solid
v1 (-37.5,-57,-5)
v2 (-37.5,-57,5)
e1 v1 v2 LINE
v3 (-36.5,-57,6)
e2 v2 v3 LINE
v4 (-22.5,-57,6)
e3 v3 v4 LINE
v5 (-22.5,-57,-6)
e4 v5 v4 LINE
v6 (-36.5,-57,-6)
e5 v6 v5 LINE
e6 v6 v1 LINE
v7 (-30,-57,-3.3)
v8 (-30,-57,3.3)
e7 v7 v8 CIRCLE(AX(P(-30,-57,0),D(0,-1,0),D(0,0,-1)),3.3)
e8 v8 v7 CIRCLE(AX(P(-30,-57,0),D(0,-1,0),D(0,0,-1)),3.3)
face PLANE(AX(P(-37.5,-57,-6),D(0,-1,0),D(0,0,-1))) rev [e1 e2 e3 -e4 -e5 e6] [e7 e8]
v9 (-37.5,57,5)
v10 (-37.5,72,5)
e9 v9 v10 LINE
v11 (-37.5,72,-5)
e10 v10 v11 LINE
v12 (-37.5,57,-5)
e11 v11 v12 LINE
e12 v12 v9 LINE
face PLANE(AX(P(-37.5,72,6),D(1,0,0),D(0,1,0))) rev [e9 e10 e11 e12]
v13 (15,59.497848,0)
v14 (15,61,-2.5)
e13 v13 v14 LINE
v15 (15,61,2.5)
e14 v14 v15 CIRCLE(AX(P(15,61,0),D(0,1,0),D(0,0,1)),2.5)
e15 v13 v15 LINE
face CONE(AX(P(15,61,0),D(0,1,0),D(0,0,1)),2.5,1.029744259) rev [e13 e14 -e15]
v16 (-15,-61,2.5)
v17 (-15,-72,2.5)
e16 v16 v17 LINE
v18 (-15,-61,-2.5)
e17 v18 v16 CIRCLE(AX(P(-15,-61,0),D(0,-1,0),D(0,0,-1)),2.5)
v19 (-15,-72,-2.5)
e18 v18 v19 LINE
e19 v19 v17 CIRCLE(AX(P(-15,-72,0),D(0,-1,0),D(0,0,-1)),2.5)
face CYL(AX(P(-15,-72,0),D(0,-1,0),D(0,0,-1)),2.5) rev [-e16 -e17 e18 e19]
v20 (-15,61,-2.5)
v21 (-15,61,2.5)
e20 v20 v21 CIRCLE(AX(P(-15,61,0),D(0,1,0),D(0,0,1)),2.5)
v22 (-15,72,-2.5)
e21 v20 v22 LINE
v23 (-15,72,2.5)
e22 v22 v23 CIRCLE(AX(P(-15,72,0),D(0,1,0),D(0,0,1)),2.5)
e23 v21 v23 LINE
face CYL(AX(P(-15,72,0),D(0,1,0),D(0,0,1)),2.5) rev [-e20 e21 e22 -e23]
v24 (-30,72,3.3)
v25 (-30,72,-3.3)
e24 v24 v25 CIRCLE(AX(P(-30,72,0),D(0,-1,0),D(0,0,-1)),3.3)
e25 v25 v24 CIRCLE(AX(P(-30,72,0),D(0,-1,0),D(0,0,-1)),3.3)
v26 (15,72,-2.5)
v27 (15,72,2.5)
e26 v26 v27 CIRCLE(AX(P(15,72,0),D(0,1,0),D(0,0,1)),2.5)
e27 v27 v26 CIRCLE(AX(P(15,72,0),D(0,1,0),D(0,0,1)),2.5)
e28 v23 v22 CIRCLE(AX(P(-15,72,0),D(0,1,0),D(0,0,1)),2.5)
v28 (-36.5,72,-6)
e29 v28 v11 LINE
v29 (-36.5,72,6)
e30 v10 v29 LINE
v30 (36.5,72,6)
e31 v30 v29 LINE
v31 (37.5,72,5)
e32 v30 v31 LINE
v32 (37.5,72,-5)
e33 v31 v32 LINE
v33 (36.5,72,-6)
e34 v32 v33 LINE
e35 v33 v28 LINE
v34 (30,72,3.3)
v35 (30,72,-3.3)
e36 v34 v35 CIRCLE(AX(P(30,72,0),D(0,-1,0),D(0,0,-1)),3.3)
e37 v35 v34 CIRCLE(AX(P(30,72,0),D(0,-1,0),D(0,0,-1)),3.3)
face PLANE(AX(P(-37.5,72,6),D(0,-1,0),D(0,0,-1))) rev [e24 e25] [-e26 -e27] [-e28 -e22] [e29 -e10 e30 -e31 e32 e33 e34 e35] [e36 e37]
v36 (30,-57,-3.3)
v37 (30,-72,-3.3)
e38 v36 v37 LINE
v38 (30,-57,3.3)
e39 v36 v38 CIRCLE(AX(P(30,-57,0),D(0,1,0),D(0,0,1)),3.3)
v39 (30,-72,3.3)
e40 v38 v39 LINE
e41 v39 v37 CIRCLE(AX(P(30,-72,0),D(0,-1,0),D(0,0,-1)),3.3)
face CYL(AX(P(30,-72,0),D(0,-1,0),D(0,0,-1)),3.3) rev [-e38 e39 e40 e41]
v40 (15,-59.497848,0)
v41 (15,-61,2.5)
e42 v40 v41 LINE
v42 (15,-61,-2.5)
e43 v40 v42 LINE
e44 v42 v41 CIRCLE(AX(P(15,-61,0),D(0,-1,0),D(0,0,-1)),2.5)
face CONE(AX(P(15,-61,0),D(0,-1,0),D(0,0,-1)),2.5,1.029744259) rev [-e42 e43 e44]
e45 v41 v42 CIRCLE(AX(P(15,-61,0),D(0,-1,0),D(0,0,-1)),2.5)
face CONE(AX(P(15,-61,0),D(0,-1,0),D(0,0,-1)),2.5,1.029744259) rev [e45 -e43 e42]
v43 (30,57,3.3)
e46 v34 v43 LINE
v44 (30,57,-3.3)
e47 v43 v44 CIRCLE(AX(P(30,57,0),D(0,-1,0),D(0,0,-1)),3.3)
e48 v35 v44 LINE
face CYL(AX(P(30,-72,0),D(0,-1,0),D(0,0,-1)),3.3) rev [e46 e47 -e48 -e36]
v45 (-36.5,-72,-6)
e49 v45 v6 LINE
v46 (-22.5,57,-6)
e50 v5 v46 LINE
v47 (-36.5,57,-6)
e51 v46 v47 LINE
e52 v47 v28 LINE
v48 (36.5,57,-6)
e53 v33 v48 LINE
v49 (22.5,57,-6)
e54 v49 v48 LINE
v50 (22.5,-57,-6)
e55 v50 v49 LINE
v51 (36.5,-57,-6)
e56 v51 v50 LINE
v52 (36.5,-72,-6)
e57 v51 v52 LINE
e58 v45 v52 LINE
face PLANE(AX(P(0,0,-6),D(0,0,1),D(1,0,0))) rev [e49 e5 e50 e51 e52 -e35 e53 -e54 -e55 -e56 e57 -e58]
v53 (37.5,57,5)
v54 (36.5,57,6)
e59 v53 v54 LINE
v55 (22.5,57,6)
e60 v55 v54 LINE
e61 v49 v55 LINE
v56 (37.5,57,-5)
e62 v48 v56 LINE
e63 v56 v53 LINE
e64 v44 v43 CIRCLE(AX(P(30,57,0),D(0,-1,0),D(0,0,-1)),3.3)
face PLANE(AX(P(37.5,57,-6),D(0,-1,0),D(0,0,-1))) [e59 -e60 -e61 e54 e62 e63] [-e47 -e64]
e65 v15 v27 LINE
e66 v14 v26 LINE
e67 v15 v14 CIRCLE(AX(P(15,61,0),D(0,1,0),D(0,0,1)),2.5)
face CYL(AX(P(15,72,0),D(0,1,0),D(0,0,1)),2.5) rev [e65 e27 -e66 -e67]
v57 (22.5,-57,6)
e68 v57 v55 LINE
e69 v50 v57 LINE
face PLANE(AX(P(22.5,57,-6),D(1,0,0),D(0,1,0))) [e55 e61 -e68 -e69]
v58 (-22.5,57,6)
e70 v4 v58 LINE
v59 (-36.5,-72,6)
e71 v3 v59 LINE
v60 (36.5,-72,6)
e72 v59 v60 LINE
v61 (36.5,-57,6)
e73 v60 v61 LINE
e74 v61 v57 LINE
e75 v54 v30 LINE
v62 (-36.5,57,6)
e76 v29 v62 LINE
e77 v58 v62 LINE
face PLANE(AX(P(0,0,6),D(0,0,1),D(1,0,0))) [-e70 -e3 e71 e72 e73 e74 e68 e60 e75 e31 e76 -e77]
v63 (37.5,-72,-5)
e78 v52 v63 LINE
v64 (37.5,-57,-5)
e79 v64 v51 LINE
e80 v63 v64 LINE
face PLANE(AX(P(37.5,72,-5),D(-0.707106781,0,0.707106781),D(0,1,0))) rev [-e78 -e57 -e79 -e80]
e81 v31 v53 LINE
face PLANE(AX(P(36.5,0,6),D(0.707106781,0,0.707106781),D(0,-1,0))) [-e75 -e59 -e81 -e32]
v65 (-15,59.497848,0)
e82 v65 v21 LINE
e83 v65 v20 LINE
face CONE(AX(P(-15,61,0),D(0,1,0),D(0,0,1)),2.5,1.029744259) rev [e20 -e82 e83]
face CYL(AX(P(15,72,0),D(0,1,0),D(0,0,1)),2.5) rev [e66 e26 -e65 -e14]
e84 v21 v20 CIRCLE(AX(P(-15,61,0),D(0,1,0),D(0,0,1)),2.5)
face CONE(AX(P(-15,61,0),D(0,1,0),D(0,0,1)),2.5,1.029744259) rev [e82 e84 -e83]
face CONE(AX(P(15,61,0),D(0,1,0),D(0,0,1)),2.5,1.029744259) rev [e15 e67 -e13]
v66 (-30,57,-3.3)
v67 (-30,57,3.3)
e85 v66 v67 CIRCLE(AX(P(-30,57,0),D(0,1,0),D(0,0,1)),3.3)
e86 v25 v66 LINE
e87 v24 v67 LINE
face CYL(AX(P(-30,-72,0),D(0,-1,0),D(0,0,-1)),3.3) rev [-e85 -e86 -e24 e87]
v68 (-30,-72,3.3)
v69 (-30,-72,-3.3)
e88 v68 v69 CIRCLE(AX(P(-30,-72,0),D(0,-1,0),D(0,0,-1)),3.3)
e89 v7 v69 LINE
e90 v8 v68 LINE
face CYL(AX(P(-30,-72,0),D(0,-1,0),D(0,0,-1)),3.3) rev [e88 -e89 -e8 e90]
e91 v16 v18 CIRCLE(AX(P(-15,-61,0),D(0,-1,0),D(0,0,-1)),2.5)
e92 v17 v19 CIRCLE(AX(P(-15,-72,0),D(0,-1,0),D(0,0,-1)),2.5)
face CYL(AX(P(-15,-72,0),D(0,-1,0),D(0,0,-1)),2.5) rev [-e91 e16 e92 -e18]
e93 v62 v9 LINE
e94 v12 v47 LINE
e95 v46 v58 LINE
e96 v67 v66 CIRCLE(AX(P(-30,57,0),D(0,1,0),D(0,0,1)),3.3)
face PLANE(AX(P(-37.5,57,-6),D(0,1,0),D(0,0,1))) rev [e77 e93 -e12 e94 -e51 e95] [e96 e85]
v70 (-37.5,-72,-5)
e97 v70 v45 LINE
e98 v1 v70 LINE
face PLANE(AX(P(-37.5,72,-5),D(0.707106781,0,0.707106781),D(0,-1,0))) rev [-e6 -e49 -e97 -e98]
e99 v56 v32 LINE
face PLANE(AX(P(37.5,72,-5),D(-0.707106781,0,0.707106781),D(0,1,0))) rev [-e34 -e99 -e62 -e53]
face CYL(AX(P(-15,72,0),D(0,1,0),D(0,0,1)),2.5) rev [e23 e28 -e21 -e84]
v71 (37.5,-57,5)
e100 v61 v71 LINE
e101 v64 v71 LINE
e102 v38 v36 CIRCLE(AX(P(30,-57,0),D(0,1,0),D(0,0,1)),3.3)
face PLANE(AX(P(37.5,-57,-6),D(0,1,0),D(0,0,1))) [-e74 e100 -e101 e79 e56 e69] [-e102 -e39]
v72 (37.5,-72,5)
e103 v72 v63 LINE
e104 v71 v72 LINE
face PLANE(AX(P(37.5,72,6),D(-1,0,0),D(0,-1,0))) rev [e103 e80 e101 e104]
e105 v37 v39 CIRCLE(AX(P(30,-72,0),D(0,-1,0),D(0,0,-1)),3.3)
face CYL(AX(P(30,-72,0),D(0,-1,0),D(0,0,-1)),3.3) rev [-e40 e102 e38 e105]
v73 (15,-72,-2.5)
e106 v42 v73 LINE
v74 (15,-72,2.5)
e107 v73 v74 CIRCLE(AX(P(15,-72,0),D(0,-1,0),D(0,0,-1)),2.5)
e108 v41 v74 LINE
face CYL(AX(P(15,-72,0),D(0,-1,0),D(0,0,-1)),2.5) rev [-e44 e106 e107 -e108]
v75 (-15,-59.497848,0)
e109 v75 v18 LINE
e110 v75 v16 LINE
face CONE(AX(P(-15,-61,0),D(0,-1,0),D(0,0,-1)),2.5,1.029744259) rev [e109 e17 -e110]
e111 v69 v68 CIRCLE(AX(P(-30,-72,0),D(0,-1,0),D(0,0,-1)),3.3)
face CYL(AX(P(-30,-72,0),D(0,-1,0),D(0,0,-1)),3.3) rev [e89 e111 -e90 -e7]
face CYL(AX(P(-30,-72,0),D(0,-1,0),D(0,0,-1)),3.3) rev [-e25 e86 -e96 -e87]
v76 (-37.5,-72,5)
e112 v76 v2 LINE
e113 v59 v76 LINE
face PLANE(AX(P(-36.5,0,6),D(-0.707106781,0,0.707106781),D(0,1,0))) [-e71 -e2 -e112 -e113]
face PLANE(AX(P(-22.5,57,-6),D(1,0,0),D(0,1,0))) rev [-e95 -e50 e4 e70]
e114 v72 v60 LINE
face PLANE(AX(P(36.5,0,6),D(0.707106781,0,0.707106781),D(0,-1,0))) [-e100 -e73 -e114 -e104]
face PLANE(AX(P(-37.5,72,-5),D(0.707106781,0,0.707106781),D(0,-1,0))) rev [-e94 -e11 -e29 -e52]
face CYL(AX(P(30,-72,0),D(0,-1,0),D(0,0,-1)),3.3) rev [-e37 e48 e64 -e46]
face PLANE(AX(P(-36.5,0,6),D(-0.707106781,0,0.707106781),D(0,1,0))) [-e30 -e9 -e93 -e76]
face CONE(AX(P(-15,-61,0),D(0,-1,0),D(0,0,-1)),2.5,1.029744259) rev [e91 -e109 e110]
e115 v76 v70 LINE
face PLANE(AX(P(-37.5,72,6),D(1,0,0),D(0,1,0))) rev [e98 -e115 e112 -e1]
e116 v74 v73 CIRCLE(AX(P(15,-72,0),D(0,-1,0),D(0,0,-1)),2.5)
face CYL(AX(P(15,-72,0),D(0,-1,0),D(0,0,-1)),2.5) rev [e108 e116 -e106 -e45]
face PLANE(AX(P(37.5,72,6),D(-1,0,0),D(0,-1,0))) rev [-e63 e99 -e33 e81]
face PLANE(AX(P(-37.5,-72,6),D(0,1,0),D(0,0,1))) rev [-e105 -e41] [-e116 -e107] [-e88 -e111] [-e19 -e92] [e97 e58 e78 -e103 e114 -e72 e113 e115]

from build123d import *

# Parameters (mm, degrees)
SKETCH1_W                          = 75
SKETCH1_H                          = 144
BOSS_EXTRUDE1_DEPTH                = 6
SKETCH4_W                          = 15
SKETCH4_H                          = 114
CUT_EXTRUDE1_DEPTH                 = 83.0624762
F_6_6_6_6_DIAMETER_HOLE1_D         = 6.6
BLIND_PIN_HOLE1_SIZE_MM_AT_2_COUNT = 2
BLIND_PIN_HOLE1_SIZE_MM_AT_2_PITCH = 30
CHAMFER1_SIZE                      = 1


with BuildPart() as part:
    # Sketch1 → Boss-Extrude1 (new, symmetric)
    with BuildSketch(Plane.XY):
        Rectangle(SKETCH1_W, SKETCH1_H)
    extrude(amount=BOSS_EXTRUDE1_DEPTH, both=True)

    # Sketch4 → Cut-Extrude1 (cut, through all)
    with BuildSketch(Plane.XY.offset(6)):
        with Locations((-30, 0)):
            Rectangle(SKETCH4_W, SKETCH4_H)
    cut_extrude1 = extrude(amount=-CUT_EXTRUDE1_DEPTH, mode=Mode.SUBTRACT)

    # Mirror1: Cut-Extrude1 across plane
    add(cut_extrude1.mirror(Plane(origin=(0, 0, 0), x_dir=(0, 0, 1), z_dir=(1, 0, 0))), mode=Mode.SUBTRACT)

    # Ø6.6 (6.6) Diameter Hole1 (through all)
    with Locations(Plane(origin=(0, -72, 0), x_dir=(-1, 0, 0), z_dir=(0, -1, 0))):
        with Locations((-30, 0), (30, 0)):
            Hole(F_6_6_6_6_DIAMETER_HOLE1_D / 2)

    # Sketch8 → Blind Pin Hole1 (size mm) (revolve, cut)
    with BuildSketch(Plane(origin=(15, -72, 0), x_dir=(0, 0, -1), z_dir=(1, 0, 0))):
        Polygon((0, 0), (0, 12.502151548), (2.5, 11), (2.5, 0), align=None)
    blind_pin_hole1_size_mm = revolve(axis=Axis((15, -78.35, 0), (0, 1, 0)), mode=Mode.SUBTRACT)

    # Blind Pin Hole1 (size mm) at 2: Blind Pin Hole1 (size mm) ×2
    with Locations(*[(-i * BLIND_PIN_HOLE1_SIZE_MM_AT_2_PITCH, 0, 0) for i in range(1, BLIND_PIN_HOLE1_SIZE_MM_AT_2_COUNT)]):
        add(blind_pin_hole1_size_mm, mode=Mode.SUBTRACT)

    # Mirror2: Blind Pin Hole1 (size mm) across plane
    add(blind_pin_hole1_size_mm.mirror(Plane.ZX), mode=Mode.SUBTRACT)

    # Mirror2 copy 1 sketch → Mirror2 copy 1 (revolve, cut)
    with BuildSketch(Plane(origin=(-15, 72, 0), x_dir=(0, 0, -1), z_dir=(1, 0, 0))):
        Polygon((0, 0), (0, -12.502151548), (2.5, -11), (2.5, 0), align=None)
    revolve(axis=Axis((-15, 78.35, 0), (0, 1, 0)), mode=Mode.SUBTRACT)

    # Chamfer1
    chamfer1_edges = [part.edges().sort_by_distance(p)[0] for p in [
        (-37.5, 64.5, 6),
        (-37.5, -64.5, -6),
        (-37.5, -64.5, 6),
        (37.5, 64.5, -6),
        (37.5, 64.5, 6),
        (37.5, -64.5, 6),
        (-37.5, 64.5, -6),
        (37.5, -64.5, -6),
    ]]
    chamfer(chamfer1_edges, length=CHAMFER1_SIZE)


solid = part.part
